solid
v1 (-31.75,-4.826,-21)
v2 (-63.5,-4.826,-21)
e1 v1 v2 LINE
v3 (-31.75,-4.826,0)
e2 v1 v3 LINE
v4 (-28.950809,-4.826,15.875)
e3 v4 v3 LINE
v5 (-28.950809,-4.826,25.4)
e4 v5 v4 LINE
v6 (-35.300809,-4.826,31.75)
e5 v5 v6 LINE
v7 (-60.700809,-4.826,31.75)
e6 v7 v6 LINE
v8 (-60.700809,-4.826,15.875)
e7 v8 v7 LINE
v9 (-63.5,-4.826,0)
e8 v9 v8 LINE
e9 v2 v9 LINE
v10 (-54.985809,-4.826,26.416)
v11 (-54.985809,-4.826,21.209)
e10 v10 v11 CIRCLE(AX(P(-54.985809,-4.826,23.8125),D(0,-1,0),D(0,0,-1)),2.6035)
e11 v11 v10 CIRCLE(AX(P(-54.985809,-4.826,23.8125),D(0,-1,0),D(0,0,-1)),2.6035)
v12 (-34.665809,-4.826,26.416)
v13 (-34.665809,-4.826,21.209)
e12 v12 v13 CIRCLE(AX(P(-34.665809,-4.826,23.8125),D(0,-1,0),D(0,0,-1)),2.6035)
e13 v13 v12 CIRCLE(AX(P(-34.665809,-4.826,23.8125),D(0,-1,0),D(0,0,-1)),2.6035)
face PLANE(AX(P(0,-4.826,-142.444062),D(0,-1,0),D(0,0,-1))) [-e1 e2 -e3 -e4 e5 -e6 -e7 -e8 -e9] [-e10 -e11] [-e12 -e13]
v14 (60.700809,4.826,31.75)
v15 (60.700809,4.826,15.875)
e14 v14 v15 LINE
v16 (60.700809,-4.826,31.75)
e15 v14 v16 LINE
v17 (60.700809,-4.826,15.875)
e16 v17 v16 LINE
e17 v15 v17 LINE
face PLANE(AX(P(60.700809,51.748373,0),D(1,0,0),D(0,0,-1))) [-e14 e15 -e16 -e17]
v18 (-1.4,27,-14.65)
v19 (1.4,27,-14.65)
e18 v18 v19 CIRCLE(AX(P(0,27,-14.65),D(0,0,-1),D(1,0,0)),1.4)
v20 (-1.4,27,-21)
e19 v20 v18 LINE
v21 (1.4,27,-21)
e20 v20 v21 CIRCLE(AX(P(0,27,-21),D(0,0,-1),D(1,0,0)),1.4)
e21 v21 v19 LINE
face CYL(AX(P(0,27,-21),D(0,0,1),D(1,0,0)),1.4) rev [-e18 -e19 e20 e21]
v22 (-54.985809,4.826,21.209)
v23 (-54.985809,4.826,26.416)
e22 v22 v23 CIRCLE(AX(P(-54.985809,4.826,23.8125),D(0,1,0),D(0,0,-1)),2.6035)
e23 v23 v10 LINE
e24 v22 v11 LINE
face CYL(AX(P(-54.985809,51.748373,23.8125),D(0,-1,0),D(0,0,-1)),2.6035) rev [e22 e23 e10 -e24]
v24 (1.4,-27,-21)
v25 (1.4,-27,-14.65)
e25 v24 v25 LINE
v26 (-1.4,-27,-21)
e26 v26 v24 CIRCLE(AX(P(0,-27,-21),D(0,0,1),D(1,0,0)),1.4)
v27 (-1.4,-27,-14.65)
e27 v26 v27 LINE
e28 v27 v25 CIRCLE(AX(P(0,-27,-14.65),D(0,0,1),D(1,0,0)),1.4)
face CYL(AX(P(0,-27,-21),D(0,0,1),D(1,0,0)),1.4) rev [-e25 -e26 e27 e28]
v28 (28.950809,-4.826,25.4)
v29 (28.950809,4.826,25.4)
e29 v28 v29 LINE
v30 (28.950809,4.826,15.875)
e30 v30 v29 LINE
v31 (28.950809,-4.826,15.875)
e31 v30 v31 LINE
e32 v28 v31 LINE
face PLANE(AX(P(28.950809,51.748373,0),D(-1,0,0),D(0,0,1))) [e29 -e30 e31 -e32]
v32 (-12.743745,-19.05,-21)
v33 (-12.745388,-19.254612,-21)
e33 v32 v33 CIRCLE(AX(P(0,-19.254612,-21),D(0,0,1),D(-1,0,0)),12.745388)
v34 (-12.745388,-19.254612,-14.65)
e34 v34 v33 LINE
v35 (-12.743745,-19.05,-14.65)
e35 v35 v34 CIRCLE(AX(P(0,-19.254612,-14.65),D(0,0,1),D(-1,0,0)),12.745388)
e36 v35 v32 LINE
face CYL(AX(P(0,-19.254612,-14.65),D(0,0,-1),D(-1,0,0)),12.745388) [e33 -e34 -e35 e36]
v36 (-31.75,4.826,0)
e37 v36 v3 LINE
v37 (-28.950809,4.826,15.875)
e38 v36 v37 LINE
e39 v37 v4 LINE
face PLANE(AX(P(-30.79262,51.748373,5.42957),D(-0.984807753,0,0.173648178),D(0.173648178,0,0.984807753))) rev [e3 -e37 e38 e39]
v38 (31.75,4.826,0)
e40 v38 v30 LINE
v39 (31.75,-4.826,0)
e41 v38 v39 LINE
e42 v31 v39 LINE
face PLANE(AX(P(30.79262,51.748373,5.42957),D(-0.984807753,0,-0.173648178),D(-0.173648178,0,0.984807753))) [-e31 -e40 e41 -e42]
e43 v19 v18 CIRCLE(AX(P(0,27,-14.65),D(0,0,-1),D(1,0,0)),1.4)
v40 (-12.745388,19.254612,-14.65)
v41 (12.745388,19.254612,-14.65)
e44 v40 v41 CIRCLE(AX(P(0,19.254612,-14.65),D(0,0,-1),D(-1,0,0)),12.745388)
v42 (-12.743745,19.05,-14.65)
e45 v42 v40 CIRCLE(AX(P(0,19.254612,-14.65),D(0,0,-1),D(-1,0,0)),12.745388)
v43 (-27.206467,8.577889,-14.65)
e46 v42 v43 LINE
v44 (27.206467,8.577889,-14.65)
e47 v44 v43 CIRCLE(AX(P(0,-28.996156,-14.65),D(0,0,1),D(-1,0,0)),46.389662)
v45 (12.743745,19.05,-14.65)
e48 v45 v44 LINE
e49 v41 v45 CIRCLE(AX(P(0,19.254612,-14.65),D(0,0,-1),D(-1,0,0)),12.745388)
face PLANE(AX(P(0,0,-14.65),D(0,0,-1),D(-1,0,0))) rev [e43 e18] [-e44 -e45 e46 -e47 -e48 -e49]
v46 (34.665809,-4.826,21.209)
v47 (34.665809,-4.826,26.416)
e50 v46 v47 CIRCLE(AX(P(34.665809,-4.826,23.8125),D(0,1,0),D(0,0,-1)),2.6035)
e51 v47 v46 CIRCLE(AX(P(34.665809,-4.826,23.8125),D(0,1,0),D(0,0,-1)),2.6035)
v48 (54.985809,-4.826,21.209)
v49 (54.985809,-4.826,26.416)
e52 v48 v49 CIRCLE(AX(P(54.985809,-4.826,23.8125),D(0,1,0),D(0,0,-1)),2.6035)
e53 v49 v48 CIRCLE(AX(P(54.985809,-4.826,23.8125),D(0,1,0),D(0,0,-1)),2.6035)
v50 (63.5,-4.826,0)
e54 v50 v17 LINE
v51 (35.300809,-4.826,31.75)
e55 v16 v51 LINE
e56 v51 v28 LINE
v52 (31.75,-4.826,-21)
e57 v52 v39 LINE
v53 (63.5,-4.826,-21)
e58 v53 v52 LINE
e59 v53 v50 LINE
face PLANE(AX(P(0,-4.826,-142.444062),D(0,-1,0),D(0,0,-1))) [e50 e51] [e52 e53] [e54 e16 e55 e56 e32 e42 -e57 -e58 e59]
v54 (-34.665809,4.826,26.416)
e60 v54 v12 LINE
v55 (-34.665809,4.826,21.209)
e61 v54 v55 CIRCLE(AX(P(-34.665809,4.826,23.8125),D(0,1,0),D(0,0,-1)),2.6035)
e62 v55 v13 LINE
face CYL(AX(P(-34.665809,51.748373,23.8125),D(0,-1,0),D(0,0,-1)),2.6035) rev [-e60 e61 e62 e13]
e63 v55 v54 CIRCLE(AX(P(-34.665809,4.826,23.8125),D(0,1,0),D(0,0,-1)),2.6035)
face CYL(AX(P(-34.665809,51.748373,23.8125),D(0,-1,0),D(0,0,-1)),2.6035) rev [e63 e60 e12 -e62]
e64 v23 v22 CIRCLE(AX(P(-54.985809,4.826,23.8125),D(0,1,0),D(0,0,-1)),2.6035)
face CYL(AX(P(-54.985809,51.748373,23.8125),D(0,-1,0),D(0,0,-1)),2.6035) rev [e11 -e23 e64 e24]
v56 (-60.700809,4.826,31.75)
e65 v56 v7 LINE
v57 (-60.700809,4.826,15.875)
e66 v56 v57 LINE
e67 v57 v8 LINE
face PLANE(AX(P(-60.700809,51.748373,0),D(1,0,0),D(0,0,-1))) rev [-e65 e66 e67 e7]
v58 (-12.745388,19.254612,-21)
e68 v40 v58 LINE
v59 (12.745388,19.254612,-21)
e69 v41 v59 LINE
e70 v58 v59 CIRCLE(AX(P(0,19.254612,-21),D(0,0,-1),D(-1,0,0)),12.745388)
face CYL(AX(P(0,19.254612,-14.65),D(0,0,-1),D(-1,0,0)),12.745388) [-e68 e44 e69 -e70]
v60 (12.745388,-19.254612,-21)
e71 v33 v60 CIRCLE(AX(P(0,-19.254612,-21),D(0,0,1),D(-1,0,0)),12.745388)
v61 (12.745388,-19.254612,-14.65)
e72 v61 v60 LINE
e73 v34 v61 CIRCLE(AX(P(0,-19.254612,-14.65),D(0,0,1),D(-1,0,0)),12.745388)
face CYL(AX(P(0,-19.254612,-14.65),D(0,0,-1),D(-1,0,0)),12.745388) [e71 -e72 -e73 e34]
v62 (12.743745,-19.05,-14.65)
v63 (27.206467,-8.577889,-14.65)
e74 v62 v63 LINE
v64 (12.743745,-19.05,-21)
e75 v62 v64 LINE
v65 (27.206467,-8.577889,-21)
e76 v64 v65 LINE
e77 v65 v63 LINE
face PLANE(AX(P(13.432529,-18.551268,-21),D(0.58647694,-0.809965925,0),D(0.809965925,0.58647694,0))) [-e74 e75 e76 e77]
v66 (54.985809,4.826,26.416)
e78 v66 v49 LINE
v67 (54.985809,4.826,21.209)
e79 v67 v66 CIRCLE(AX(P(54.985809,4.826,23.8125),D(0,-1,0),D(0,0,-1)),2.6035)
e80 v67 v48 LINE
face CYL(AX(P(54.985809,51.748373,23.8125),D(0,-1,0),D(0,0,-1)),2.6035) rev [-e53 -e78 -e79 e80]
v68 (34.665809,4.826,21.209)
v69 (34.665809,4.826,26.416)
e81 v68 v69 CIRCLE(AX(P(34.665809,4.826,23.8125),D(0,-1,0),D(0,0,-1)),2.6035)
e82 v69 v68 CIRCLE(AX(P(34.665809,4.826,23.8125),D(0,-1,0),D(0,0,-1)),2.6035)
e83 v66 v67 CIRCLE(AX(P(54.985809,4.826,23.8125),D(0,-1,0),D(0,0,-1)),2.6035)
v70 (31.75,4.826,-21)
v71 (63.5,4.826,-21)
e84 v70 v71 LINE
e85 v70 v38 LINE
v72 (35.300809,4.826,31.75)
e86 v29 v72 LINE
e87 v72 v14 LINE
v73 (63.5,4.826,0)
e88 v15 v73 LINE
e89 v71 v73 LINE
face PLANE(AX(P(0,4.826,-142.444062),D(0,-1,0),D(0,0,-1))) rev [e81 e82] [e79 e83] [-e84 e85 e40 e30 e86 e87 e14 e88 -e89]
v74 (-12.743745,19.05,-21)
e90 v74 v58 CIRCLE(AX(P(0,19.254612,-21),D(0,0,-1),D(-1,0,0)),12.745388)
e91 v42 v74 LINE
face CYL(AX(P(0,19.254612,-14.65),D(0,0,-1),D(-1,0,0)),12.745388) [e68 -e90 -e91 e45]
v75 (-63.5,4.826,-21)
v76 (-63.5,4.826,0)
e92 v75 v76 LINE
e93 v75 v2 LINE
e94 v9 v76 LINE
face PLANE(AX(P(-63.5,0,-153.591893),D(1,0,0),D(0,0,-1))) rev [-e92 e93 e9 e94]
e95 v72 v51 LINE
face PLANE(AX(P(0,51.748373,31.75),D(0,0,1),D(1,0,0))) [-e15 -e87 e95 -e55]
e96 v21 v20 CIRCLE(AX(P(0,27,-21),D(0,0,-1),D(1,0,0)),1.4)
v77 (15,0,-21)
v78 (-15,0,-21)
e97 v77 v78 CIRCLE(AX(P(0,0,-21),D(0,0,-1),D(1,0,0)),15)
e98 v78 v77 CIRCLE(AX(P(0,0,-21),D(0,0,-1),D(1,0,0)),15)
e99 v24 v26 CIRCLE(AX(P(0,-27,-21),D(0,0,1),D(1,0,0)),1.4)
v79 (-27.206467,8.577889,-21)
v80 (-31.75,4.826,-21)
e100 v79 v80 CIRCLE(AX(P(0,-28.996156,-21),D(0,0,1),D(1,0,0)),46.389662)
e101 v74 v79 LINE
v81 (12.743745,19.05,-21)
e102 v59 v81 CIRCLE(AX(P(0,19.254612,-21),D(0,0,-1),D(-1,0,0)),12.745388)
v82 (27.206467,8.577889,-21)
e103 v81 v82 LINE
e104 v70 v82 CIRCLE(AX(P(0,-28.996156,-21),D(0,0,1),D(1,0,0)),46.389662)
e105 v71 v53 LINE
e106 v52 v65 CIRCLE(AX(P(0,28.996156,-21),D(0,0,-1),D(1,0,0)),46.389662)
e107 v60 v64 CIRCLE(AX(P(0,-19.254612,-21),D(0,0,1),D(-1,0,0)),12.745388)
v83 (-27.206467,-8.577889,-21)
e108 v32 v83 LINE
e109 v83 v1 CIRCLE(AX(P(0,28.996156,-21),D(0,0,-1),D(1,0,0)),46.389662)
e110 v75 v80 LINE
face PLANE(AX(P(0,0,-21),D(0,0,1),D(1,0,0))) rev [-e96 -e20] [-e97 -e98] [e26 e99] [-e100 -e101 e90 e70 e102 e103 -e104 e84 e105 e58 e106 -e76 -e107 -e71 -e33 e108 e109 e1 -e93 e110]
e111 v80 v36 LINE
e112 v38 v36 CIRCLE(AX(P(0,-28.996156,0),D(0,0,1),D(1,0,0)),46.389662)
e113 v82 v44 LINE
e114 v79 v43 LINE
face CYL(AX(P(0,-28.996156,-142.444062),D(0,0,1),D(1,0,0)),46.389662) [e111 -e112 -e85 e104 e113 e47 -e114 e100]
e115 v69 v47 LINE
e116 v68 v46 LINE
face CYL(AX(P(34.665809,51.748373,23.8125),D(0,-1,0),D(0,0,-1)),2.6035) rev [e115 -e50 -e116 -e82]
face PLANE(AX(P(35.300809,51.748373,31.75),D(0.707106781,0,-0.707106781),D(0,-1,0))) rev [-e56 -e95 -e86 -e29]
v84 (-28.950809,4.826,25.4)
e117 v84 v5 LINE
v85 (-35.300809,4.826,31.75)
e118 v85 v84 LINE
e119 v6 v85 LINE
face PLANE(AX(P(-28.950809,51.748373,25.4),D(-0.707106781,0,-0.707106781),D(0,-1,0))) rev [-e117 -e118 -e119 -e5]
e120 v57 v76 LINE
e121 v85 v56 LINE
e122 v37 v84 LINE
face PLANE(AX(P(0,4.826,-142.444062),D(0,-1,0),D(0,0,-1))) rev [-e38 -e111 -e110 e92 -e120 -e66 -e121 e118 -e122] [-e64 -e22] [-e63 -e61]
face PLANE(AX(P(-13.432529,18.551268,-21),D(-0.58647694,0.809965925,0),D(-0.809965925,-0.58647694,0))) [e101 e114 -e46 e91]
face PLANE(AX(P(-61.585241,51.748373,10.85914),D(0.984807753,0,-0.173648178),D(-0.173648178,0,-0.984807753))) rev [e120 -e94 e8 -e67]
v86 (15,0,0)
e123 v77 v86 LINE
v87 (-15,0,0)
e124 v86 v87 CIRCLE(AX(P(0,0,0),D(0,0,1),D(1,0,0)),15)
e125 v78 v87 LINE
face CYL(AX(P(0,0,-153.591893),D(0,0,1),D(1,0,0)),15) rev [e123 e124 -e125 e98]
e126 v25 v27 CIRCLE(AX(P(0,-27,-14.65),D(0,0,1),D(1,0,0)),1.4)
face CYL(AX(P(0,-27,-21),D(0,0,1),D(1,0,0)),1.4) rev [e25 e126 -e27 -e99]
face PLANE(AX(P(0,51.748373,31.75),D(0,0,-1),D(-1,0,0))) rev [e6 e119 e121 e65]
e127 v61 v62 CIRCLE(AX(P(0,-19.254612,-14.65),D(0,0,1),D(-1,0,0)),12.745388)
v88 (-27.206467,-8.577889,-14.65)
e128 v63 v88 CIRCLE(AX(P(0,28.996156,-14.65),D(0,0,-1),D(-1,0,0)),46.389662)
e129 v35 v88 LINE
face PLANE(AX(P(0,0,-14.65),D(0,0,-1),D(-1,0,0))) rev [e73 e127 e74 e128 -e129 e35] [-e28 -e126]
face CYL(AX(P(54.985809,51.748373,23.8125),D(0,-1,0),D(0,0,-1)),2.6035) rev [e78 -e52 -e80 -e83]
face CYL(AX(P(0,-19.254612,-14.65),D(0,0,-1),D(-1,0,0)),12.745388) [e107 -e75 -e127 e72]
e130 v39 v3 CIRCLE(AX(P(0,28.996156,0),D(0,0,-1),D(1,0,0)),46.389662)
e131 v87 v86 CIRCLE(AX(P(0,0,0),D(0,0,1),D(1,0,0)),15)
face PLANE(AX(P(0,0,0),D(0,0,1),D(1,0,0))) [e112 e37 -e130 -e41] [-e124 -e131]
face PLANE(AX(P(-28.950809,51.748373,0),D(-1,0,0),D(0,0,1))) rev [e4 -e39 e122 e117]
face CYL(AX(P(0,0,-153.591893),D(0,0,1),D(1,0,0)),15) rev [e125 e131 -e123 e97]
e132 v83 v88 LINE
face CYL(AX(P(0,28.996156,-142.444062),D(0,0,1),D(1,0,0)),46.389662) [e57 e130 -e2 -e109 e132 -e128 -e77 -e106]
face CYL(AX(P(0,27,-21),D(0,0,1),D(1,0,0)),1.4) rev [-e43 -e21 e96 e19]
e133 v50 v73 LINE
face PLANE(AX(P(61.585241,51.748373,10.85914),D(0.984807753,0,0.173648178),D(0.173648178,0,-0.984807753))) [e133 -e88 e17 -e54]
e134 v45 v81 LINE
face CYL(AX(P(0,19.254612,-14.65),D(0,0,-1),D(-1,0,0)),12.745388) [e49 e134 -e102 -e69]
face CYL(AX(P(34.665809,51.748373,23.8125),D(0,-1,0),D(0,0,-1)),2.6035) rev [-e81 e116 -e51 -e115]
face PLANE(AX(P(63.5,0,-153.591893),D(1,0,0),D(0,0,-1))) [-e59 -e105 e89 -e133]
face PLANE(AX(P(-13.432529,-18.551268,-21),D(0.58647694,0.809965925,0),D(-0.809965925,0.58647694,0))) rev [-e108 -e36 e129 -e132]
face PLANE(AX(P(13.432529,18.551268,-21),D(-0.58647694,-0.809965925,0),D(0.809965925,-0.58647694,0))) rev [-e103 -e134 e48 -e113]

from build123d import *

# Parameters (mm, degrees)
SKETCH1_W           = 127
SKETCH1_H           = 38.1
SKETCH1_R           = 15
BOSS_EXTRUDE1_DEPTH = 21
BOSS_EXTRUDE2_DEPTH = 6.35
SKETCH4_R           = 1.4
CUT_EXTRUDE2_DEPTH  = 6.35
CUT_EXTRUDE6_DEPTH  = 14.65
CUT_EXTRUDE7_DEPTH  = 73.600774789
SKETCH7_R           = 2.6035
CUT_EXTRUDE8_DEPTH  = 22.86
SKETCH8_W           = 31.75
SKETCH8_H           = 15.875
SKETCH8_R           = 2.6035
BOSS_EXTRUDE3_DEPTH = 9.652
CHAMFER1_SIZE       = 6.35
BOSS_EXTRUDE4_START = -9.652
SKETCH9_W           = 26.681402361
SKETCH9_H           = 11.886393241
SKETCH9_R           = 2.6035
SKETCH9_W_2         = 26.993648234
BOSS_EXTRUDE4_DEPTH = 9.652


with BuildPart() as part:
    # Sketch1 → Boss-Extrude1 (new body)
    with BuildSketch(Plane.XY):
        Rectangle(SKETCH1_W, SKETCH1_H)
        Circle(SKETCH1_R, mode=Mode.SUBTRACT)
    extrude(amount=-BOSS_EXTRUDE1_DEPTH)

    # Sketch3 → Boss-Extrude2 (add)
    with BuildSketch(Plane(origin=(0, 0, -21), x_dir=(-1, 0, 0), z_dir=(0, 0, -1))):
        with BuildLine():
            Line((12.743745366, -19.05), (-12.743745366, -19.05))
            ThreePointArc((-12.743745366, -19.05), (-9.084403439, -28.194328353), (1.02e-07, -32))
            ThreePointArc((1.02e-07, -32), (9.08440351, -28.194328281), (12.743745366, -19.05))
        make_face()
    boss_extrude2 = extrude(amount=-BOSS_EXTRUDE2_DEPTH)

    # Sketch4 → Cut-Extrude2 (cut)
    with BuildSketch(Plane.XY.offset(-14.65)):
        with Locations((0, -27)):
            Circle(SKETCH4_R)
    cut_extrude2 = extrude(amount=-CUT_EXTRUDE2_DEPTH, mode=Mode.SUBTRACT)

    # Mirror1: Boss-Extrude2, Cut-Extrude2 across plane
    add(boss_extrude2.mirror(Plane.ZX))
    add(cut_extrude2.mirror(Plane.ZX), mode=Mode.SUBTRACT)

    # Sketch5 → Cut-Extrude6 (cut)
    with BuildSketch(Plane.XY):
        with BuildLine():
            Line((-31.75, -4.826), (-63.5, -4.826))
            Line((-63.5, -4.826), (-63.5, -19.05))
            Line((-63.5, -19.05), (63.5, -19.05))
            Line((63.5, -19.05), (63.5, -4.826))
            Line((63.5, -4.826), (31.75, -4.826))
            ThreePointArc((31.75, -4.826), (0, -17.39350594), (-31.75, -4.826))
        make_face()
        with BuildLine():
            Line((-63.5, 19.05), (-63.5, 4.826))
            Line((-63.5, 4.826), (-31.75, 4.826))
            ThreePointArc((-31.75, 4.826), (0, 17.39350594), (31.75, 4.826))
            Line((31.75, 4.826), (63.5, 4.826))
            Line((63.5, 4.826), (63.5, 19.05))
            Line((63.5, 19.05), (-63.5, 19.05))
        make_face()
    extrude(amount=-CUT_EXTRUDE6_DEPTH, mode=Mode.SUBTRACT)

    # Sketch6 → Cut-Extrude7 (cut, through all)
    with BuildSketch(Plane.XY.offset(-14.65)):
        with BuildLine():
            Line((27.206467014, -8.577889412), (12.743745366, -19.05))
            Line((12.743745366, -19.05), (63.5, -19.05))
            Line((63.5, -19.05), (63.5, -4.826))
            Line((63.5, -4.826), (31.75, -4.826))
            ThreePointArc((31.75, -4.826), (29.537864162, -6.774157348), (27.206467014, -8.577889412))
        make_face()
        with BuildLine():
            Line((-63.5, -19.05), (-12.743745366, -19.05))
            Line((-12.743745366, -19.05), (-27.206467014, -8.577889412))
            ThreePointArc((-27.206467014, -8.577889412), (-29.537864162, -6.774157348), (-31.75, -4.826))
            Line((-31.75, -4.826), (-63.5, -4.826))
            Line((-63.5, -4.826), (-63.5, -19.05))
        make_face()
        with BuildLine():
            Line((-27.206467014, 8.577889412), (-12.743745366, 19.05))
            Line((-12.743745366, 19.05), (-63.5, 19.05))
            Line((-63.5, 19.05), (-63.5, 4.826))
            Line((-63.5, 4.826), (-31.75, 4.826))
            ThreePointArc((-31.75, 4.826), (-29.537864162, 6.774157348), (-27.206467014, 8.577889412))
        make_face()
        with BuildLine():
            Line((63.5, 19.05), (12.743745366, 19.05))
            Line((12.743745366, 19.05), (27.206467014, 8.577889412))
            ThreePointArc((27.206467014, 8.577889412), (29.537864162, 6.774157348), (31.75, 4.826))
            Line((31.75, 4.826), (63.5, 4.826))
            Line((63.5, 4.826), (63.5, 19.05))
        make_face()
    extrude(amount=-CUT_EXTRUDE7_DEPTH, mode=Mode.SUBTRACT)

    # Sketch7 → Cut-Extrude8 (cut)
    with BuildSketch(Plane(origin=(0, 4.826, 0), x_dir=(1, 0, 0), z_dir=(0, 1, 0))):
        with Locations(Location((-57.785, 10.5, 0), (0, 0, 270))):
            Circle(SKETCH7_R)
        with Locations(Location((-37.465, 10.5, 0), (0, 0, 270))):
            Circle(SKETCH7_R)
        with Locations(Location((37.465, 10.5, 0), (0, 0, 270))):
            Circle(SKETCH7_R)
        with Locations(Location((57.785, 10.5, 0), (0, 0, 270))):
            Circle(SKETCH7_R)
    extrude(amount=-CUT_EXTRUDE8_DEPTH, mode=Mode.SUBTRACT)

    # Sketch8 → Boss-Extrude3 (add)
    # profile 1 of 4: a face of its own
    with BuildSketch(Plane.XZ.offset(4.826)):
        Polygon((63.5, 0), (31.75, 0), (28.950809181, 15.875), (60.700809181, 15.875), align=None)
    # profile 2 of 4: a face of its own
    with BuildSketch(Plane.XZ.offset(4.826)):
        with Locations((44.825809181, 23.8125)):
            Rectangle(SKETCH8_W, SKETCH8_H)
        with Locations(Location((34.665809181, 23.8125, 0), (0, 0, 270))):
            Circle(SKETCH8_R, mode=Mode.SUBTRACT)
        with Locations(Location((54.985809181, 23.8125, 0), (0, 0, 270))):
            Circle(SKETCH8_R, mode=Mode.SUBTRACT)
    # profile 3 of 4: a face of its own
    with BuildSketch(Plane.XZ.offset(4.826)):
        with Locations((-44.825809181, 23.8125)):
            Rectangle(SKETCH8_W, SKETCH8_H)
        with Locations(Location((-34.665809181, 23.8125, 0), (0, 0, 270))):
            Circle(SKETCH8_R, mode=Mode.SUBTRACT)
        with Locations(Location((-54.985809181, 23.8125, 0), (0, 0, 270))):
            Circle(SKETCH8_R, mode=Mode.SUBTRACT)
    # profile 4 of 4: a face of its own
    with BuildSketch(Plane.XZ.offset(4.826)):
        Polygon((-60.700809181, 15.875), (-28.950809181, 15.875), (-31.75, 0), (-63.5, 0), align=None)
    extrude(amount=-BOSS_EXTRUDE3_DEPTH)

    # Chamfer1
    chamfer1_edges = [part.edges().sort_by_distance(p)[0] for p in [
        (28.950809181, 0, 31.75),
        (-28.950809181, 0, 31.75),
    ]]
    chamfer(chamfer1_edges, length=CHAMFER1_SIZE)

    # Sketch9 → Boss-Extrude4 (add)
    # profile 1 of 4: a face of its own
    with BuildSketch(Plane.XZ.offset(4.826).offset(BOSS_EXTRUDE4_START)):
        with Locations((-47.360108001, -9.539491199)):
            Rectangle(SKETCH9_W, SKETCH9_H)
        with Locations((-57.785, -10.5)):
            Circle(SKETCH9_R, mode=Mode.SUBTRACT)
        with Locations((-37.465, -10.5)):
            Circle(SKETCH9_R, mode=Mode.SUBTRACT)
    # profile 2 of 4: a face of its own
    with BuildSketch(Plane.XZ.offset(4.826).offset(BOSS_EXTRUDE4_START)):
        with Locations((-57.785, -10.5)):
            Circle(SKETCH9_R)
    # profile 3 of 4: a face of its own
    with BuildSketch(Plane.XZ.offset(4.826).offset(BOSS_EXTRUDE4_START)):
        with Locations((-37.465, -10.5)):
            Circle(SKETCH9_R)
    # profile 4 of 4: a face of its own
    with BuildSketch(Plane.XZ.offset(4.826).offset(BOSS_EXTRUDE4_START)):
        with Locations((47.713125711, -9.539491199)):
            Rectangle(SKETCH9_W_2, SKETCH9_H)
    extrude(amount=BOSS_EXTRUDE4_DEPTH)


solid = part.part
